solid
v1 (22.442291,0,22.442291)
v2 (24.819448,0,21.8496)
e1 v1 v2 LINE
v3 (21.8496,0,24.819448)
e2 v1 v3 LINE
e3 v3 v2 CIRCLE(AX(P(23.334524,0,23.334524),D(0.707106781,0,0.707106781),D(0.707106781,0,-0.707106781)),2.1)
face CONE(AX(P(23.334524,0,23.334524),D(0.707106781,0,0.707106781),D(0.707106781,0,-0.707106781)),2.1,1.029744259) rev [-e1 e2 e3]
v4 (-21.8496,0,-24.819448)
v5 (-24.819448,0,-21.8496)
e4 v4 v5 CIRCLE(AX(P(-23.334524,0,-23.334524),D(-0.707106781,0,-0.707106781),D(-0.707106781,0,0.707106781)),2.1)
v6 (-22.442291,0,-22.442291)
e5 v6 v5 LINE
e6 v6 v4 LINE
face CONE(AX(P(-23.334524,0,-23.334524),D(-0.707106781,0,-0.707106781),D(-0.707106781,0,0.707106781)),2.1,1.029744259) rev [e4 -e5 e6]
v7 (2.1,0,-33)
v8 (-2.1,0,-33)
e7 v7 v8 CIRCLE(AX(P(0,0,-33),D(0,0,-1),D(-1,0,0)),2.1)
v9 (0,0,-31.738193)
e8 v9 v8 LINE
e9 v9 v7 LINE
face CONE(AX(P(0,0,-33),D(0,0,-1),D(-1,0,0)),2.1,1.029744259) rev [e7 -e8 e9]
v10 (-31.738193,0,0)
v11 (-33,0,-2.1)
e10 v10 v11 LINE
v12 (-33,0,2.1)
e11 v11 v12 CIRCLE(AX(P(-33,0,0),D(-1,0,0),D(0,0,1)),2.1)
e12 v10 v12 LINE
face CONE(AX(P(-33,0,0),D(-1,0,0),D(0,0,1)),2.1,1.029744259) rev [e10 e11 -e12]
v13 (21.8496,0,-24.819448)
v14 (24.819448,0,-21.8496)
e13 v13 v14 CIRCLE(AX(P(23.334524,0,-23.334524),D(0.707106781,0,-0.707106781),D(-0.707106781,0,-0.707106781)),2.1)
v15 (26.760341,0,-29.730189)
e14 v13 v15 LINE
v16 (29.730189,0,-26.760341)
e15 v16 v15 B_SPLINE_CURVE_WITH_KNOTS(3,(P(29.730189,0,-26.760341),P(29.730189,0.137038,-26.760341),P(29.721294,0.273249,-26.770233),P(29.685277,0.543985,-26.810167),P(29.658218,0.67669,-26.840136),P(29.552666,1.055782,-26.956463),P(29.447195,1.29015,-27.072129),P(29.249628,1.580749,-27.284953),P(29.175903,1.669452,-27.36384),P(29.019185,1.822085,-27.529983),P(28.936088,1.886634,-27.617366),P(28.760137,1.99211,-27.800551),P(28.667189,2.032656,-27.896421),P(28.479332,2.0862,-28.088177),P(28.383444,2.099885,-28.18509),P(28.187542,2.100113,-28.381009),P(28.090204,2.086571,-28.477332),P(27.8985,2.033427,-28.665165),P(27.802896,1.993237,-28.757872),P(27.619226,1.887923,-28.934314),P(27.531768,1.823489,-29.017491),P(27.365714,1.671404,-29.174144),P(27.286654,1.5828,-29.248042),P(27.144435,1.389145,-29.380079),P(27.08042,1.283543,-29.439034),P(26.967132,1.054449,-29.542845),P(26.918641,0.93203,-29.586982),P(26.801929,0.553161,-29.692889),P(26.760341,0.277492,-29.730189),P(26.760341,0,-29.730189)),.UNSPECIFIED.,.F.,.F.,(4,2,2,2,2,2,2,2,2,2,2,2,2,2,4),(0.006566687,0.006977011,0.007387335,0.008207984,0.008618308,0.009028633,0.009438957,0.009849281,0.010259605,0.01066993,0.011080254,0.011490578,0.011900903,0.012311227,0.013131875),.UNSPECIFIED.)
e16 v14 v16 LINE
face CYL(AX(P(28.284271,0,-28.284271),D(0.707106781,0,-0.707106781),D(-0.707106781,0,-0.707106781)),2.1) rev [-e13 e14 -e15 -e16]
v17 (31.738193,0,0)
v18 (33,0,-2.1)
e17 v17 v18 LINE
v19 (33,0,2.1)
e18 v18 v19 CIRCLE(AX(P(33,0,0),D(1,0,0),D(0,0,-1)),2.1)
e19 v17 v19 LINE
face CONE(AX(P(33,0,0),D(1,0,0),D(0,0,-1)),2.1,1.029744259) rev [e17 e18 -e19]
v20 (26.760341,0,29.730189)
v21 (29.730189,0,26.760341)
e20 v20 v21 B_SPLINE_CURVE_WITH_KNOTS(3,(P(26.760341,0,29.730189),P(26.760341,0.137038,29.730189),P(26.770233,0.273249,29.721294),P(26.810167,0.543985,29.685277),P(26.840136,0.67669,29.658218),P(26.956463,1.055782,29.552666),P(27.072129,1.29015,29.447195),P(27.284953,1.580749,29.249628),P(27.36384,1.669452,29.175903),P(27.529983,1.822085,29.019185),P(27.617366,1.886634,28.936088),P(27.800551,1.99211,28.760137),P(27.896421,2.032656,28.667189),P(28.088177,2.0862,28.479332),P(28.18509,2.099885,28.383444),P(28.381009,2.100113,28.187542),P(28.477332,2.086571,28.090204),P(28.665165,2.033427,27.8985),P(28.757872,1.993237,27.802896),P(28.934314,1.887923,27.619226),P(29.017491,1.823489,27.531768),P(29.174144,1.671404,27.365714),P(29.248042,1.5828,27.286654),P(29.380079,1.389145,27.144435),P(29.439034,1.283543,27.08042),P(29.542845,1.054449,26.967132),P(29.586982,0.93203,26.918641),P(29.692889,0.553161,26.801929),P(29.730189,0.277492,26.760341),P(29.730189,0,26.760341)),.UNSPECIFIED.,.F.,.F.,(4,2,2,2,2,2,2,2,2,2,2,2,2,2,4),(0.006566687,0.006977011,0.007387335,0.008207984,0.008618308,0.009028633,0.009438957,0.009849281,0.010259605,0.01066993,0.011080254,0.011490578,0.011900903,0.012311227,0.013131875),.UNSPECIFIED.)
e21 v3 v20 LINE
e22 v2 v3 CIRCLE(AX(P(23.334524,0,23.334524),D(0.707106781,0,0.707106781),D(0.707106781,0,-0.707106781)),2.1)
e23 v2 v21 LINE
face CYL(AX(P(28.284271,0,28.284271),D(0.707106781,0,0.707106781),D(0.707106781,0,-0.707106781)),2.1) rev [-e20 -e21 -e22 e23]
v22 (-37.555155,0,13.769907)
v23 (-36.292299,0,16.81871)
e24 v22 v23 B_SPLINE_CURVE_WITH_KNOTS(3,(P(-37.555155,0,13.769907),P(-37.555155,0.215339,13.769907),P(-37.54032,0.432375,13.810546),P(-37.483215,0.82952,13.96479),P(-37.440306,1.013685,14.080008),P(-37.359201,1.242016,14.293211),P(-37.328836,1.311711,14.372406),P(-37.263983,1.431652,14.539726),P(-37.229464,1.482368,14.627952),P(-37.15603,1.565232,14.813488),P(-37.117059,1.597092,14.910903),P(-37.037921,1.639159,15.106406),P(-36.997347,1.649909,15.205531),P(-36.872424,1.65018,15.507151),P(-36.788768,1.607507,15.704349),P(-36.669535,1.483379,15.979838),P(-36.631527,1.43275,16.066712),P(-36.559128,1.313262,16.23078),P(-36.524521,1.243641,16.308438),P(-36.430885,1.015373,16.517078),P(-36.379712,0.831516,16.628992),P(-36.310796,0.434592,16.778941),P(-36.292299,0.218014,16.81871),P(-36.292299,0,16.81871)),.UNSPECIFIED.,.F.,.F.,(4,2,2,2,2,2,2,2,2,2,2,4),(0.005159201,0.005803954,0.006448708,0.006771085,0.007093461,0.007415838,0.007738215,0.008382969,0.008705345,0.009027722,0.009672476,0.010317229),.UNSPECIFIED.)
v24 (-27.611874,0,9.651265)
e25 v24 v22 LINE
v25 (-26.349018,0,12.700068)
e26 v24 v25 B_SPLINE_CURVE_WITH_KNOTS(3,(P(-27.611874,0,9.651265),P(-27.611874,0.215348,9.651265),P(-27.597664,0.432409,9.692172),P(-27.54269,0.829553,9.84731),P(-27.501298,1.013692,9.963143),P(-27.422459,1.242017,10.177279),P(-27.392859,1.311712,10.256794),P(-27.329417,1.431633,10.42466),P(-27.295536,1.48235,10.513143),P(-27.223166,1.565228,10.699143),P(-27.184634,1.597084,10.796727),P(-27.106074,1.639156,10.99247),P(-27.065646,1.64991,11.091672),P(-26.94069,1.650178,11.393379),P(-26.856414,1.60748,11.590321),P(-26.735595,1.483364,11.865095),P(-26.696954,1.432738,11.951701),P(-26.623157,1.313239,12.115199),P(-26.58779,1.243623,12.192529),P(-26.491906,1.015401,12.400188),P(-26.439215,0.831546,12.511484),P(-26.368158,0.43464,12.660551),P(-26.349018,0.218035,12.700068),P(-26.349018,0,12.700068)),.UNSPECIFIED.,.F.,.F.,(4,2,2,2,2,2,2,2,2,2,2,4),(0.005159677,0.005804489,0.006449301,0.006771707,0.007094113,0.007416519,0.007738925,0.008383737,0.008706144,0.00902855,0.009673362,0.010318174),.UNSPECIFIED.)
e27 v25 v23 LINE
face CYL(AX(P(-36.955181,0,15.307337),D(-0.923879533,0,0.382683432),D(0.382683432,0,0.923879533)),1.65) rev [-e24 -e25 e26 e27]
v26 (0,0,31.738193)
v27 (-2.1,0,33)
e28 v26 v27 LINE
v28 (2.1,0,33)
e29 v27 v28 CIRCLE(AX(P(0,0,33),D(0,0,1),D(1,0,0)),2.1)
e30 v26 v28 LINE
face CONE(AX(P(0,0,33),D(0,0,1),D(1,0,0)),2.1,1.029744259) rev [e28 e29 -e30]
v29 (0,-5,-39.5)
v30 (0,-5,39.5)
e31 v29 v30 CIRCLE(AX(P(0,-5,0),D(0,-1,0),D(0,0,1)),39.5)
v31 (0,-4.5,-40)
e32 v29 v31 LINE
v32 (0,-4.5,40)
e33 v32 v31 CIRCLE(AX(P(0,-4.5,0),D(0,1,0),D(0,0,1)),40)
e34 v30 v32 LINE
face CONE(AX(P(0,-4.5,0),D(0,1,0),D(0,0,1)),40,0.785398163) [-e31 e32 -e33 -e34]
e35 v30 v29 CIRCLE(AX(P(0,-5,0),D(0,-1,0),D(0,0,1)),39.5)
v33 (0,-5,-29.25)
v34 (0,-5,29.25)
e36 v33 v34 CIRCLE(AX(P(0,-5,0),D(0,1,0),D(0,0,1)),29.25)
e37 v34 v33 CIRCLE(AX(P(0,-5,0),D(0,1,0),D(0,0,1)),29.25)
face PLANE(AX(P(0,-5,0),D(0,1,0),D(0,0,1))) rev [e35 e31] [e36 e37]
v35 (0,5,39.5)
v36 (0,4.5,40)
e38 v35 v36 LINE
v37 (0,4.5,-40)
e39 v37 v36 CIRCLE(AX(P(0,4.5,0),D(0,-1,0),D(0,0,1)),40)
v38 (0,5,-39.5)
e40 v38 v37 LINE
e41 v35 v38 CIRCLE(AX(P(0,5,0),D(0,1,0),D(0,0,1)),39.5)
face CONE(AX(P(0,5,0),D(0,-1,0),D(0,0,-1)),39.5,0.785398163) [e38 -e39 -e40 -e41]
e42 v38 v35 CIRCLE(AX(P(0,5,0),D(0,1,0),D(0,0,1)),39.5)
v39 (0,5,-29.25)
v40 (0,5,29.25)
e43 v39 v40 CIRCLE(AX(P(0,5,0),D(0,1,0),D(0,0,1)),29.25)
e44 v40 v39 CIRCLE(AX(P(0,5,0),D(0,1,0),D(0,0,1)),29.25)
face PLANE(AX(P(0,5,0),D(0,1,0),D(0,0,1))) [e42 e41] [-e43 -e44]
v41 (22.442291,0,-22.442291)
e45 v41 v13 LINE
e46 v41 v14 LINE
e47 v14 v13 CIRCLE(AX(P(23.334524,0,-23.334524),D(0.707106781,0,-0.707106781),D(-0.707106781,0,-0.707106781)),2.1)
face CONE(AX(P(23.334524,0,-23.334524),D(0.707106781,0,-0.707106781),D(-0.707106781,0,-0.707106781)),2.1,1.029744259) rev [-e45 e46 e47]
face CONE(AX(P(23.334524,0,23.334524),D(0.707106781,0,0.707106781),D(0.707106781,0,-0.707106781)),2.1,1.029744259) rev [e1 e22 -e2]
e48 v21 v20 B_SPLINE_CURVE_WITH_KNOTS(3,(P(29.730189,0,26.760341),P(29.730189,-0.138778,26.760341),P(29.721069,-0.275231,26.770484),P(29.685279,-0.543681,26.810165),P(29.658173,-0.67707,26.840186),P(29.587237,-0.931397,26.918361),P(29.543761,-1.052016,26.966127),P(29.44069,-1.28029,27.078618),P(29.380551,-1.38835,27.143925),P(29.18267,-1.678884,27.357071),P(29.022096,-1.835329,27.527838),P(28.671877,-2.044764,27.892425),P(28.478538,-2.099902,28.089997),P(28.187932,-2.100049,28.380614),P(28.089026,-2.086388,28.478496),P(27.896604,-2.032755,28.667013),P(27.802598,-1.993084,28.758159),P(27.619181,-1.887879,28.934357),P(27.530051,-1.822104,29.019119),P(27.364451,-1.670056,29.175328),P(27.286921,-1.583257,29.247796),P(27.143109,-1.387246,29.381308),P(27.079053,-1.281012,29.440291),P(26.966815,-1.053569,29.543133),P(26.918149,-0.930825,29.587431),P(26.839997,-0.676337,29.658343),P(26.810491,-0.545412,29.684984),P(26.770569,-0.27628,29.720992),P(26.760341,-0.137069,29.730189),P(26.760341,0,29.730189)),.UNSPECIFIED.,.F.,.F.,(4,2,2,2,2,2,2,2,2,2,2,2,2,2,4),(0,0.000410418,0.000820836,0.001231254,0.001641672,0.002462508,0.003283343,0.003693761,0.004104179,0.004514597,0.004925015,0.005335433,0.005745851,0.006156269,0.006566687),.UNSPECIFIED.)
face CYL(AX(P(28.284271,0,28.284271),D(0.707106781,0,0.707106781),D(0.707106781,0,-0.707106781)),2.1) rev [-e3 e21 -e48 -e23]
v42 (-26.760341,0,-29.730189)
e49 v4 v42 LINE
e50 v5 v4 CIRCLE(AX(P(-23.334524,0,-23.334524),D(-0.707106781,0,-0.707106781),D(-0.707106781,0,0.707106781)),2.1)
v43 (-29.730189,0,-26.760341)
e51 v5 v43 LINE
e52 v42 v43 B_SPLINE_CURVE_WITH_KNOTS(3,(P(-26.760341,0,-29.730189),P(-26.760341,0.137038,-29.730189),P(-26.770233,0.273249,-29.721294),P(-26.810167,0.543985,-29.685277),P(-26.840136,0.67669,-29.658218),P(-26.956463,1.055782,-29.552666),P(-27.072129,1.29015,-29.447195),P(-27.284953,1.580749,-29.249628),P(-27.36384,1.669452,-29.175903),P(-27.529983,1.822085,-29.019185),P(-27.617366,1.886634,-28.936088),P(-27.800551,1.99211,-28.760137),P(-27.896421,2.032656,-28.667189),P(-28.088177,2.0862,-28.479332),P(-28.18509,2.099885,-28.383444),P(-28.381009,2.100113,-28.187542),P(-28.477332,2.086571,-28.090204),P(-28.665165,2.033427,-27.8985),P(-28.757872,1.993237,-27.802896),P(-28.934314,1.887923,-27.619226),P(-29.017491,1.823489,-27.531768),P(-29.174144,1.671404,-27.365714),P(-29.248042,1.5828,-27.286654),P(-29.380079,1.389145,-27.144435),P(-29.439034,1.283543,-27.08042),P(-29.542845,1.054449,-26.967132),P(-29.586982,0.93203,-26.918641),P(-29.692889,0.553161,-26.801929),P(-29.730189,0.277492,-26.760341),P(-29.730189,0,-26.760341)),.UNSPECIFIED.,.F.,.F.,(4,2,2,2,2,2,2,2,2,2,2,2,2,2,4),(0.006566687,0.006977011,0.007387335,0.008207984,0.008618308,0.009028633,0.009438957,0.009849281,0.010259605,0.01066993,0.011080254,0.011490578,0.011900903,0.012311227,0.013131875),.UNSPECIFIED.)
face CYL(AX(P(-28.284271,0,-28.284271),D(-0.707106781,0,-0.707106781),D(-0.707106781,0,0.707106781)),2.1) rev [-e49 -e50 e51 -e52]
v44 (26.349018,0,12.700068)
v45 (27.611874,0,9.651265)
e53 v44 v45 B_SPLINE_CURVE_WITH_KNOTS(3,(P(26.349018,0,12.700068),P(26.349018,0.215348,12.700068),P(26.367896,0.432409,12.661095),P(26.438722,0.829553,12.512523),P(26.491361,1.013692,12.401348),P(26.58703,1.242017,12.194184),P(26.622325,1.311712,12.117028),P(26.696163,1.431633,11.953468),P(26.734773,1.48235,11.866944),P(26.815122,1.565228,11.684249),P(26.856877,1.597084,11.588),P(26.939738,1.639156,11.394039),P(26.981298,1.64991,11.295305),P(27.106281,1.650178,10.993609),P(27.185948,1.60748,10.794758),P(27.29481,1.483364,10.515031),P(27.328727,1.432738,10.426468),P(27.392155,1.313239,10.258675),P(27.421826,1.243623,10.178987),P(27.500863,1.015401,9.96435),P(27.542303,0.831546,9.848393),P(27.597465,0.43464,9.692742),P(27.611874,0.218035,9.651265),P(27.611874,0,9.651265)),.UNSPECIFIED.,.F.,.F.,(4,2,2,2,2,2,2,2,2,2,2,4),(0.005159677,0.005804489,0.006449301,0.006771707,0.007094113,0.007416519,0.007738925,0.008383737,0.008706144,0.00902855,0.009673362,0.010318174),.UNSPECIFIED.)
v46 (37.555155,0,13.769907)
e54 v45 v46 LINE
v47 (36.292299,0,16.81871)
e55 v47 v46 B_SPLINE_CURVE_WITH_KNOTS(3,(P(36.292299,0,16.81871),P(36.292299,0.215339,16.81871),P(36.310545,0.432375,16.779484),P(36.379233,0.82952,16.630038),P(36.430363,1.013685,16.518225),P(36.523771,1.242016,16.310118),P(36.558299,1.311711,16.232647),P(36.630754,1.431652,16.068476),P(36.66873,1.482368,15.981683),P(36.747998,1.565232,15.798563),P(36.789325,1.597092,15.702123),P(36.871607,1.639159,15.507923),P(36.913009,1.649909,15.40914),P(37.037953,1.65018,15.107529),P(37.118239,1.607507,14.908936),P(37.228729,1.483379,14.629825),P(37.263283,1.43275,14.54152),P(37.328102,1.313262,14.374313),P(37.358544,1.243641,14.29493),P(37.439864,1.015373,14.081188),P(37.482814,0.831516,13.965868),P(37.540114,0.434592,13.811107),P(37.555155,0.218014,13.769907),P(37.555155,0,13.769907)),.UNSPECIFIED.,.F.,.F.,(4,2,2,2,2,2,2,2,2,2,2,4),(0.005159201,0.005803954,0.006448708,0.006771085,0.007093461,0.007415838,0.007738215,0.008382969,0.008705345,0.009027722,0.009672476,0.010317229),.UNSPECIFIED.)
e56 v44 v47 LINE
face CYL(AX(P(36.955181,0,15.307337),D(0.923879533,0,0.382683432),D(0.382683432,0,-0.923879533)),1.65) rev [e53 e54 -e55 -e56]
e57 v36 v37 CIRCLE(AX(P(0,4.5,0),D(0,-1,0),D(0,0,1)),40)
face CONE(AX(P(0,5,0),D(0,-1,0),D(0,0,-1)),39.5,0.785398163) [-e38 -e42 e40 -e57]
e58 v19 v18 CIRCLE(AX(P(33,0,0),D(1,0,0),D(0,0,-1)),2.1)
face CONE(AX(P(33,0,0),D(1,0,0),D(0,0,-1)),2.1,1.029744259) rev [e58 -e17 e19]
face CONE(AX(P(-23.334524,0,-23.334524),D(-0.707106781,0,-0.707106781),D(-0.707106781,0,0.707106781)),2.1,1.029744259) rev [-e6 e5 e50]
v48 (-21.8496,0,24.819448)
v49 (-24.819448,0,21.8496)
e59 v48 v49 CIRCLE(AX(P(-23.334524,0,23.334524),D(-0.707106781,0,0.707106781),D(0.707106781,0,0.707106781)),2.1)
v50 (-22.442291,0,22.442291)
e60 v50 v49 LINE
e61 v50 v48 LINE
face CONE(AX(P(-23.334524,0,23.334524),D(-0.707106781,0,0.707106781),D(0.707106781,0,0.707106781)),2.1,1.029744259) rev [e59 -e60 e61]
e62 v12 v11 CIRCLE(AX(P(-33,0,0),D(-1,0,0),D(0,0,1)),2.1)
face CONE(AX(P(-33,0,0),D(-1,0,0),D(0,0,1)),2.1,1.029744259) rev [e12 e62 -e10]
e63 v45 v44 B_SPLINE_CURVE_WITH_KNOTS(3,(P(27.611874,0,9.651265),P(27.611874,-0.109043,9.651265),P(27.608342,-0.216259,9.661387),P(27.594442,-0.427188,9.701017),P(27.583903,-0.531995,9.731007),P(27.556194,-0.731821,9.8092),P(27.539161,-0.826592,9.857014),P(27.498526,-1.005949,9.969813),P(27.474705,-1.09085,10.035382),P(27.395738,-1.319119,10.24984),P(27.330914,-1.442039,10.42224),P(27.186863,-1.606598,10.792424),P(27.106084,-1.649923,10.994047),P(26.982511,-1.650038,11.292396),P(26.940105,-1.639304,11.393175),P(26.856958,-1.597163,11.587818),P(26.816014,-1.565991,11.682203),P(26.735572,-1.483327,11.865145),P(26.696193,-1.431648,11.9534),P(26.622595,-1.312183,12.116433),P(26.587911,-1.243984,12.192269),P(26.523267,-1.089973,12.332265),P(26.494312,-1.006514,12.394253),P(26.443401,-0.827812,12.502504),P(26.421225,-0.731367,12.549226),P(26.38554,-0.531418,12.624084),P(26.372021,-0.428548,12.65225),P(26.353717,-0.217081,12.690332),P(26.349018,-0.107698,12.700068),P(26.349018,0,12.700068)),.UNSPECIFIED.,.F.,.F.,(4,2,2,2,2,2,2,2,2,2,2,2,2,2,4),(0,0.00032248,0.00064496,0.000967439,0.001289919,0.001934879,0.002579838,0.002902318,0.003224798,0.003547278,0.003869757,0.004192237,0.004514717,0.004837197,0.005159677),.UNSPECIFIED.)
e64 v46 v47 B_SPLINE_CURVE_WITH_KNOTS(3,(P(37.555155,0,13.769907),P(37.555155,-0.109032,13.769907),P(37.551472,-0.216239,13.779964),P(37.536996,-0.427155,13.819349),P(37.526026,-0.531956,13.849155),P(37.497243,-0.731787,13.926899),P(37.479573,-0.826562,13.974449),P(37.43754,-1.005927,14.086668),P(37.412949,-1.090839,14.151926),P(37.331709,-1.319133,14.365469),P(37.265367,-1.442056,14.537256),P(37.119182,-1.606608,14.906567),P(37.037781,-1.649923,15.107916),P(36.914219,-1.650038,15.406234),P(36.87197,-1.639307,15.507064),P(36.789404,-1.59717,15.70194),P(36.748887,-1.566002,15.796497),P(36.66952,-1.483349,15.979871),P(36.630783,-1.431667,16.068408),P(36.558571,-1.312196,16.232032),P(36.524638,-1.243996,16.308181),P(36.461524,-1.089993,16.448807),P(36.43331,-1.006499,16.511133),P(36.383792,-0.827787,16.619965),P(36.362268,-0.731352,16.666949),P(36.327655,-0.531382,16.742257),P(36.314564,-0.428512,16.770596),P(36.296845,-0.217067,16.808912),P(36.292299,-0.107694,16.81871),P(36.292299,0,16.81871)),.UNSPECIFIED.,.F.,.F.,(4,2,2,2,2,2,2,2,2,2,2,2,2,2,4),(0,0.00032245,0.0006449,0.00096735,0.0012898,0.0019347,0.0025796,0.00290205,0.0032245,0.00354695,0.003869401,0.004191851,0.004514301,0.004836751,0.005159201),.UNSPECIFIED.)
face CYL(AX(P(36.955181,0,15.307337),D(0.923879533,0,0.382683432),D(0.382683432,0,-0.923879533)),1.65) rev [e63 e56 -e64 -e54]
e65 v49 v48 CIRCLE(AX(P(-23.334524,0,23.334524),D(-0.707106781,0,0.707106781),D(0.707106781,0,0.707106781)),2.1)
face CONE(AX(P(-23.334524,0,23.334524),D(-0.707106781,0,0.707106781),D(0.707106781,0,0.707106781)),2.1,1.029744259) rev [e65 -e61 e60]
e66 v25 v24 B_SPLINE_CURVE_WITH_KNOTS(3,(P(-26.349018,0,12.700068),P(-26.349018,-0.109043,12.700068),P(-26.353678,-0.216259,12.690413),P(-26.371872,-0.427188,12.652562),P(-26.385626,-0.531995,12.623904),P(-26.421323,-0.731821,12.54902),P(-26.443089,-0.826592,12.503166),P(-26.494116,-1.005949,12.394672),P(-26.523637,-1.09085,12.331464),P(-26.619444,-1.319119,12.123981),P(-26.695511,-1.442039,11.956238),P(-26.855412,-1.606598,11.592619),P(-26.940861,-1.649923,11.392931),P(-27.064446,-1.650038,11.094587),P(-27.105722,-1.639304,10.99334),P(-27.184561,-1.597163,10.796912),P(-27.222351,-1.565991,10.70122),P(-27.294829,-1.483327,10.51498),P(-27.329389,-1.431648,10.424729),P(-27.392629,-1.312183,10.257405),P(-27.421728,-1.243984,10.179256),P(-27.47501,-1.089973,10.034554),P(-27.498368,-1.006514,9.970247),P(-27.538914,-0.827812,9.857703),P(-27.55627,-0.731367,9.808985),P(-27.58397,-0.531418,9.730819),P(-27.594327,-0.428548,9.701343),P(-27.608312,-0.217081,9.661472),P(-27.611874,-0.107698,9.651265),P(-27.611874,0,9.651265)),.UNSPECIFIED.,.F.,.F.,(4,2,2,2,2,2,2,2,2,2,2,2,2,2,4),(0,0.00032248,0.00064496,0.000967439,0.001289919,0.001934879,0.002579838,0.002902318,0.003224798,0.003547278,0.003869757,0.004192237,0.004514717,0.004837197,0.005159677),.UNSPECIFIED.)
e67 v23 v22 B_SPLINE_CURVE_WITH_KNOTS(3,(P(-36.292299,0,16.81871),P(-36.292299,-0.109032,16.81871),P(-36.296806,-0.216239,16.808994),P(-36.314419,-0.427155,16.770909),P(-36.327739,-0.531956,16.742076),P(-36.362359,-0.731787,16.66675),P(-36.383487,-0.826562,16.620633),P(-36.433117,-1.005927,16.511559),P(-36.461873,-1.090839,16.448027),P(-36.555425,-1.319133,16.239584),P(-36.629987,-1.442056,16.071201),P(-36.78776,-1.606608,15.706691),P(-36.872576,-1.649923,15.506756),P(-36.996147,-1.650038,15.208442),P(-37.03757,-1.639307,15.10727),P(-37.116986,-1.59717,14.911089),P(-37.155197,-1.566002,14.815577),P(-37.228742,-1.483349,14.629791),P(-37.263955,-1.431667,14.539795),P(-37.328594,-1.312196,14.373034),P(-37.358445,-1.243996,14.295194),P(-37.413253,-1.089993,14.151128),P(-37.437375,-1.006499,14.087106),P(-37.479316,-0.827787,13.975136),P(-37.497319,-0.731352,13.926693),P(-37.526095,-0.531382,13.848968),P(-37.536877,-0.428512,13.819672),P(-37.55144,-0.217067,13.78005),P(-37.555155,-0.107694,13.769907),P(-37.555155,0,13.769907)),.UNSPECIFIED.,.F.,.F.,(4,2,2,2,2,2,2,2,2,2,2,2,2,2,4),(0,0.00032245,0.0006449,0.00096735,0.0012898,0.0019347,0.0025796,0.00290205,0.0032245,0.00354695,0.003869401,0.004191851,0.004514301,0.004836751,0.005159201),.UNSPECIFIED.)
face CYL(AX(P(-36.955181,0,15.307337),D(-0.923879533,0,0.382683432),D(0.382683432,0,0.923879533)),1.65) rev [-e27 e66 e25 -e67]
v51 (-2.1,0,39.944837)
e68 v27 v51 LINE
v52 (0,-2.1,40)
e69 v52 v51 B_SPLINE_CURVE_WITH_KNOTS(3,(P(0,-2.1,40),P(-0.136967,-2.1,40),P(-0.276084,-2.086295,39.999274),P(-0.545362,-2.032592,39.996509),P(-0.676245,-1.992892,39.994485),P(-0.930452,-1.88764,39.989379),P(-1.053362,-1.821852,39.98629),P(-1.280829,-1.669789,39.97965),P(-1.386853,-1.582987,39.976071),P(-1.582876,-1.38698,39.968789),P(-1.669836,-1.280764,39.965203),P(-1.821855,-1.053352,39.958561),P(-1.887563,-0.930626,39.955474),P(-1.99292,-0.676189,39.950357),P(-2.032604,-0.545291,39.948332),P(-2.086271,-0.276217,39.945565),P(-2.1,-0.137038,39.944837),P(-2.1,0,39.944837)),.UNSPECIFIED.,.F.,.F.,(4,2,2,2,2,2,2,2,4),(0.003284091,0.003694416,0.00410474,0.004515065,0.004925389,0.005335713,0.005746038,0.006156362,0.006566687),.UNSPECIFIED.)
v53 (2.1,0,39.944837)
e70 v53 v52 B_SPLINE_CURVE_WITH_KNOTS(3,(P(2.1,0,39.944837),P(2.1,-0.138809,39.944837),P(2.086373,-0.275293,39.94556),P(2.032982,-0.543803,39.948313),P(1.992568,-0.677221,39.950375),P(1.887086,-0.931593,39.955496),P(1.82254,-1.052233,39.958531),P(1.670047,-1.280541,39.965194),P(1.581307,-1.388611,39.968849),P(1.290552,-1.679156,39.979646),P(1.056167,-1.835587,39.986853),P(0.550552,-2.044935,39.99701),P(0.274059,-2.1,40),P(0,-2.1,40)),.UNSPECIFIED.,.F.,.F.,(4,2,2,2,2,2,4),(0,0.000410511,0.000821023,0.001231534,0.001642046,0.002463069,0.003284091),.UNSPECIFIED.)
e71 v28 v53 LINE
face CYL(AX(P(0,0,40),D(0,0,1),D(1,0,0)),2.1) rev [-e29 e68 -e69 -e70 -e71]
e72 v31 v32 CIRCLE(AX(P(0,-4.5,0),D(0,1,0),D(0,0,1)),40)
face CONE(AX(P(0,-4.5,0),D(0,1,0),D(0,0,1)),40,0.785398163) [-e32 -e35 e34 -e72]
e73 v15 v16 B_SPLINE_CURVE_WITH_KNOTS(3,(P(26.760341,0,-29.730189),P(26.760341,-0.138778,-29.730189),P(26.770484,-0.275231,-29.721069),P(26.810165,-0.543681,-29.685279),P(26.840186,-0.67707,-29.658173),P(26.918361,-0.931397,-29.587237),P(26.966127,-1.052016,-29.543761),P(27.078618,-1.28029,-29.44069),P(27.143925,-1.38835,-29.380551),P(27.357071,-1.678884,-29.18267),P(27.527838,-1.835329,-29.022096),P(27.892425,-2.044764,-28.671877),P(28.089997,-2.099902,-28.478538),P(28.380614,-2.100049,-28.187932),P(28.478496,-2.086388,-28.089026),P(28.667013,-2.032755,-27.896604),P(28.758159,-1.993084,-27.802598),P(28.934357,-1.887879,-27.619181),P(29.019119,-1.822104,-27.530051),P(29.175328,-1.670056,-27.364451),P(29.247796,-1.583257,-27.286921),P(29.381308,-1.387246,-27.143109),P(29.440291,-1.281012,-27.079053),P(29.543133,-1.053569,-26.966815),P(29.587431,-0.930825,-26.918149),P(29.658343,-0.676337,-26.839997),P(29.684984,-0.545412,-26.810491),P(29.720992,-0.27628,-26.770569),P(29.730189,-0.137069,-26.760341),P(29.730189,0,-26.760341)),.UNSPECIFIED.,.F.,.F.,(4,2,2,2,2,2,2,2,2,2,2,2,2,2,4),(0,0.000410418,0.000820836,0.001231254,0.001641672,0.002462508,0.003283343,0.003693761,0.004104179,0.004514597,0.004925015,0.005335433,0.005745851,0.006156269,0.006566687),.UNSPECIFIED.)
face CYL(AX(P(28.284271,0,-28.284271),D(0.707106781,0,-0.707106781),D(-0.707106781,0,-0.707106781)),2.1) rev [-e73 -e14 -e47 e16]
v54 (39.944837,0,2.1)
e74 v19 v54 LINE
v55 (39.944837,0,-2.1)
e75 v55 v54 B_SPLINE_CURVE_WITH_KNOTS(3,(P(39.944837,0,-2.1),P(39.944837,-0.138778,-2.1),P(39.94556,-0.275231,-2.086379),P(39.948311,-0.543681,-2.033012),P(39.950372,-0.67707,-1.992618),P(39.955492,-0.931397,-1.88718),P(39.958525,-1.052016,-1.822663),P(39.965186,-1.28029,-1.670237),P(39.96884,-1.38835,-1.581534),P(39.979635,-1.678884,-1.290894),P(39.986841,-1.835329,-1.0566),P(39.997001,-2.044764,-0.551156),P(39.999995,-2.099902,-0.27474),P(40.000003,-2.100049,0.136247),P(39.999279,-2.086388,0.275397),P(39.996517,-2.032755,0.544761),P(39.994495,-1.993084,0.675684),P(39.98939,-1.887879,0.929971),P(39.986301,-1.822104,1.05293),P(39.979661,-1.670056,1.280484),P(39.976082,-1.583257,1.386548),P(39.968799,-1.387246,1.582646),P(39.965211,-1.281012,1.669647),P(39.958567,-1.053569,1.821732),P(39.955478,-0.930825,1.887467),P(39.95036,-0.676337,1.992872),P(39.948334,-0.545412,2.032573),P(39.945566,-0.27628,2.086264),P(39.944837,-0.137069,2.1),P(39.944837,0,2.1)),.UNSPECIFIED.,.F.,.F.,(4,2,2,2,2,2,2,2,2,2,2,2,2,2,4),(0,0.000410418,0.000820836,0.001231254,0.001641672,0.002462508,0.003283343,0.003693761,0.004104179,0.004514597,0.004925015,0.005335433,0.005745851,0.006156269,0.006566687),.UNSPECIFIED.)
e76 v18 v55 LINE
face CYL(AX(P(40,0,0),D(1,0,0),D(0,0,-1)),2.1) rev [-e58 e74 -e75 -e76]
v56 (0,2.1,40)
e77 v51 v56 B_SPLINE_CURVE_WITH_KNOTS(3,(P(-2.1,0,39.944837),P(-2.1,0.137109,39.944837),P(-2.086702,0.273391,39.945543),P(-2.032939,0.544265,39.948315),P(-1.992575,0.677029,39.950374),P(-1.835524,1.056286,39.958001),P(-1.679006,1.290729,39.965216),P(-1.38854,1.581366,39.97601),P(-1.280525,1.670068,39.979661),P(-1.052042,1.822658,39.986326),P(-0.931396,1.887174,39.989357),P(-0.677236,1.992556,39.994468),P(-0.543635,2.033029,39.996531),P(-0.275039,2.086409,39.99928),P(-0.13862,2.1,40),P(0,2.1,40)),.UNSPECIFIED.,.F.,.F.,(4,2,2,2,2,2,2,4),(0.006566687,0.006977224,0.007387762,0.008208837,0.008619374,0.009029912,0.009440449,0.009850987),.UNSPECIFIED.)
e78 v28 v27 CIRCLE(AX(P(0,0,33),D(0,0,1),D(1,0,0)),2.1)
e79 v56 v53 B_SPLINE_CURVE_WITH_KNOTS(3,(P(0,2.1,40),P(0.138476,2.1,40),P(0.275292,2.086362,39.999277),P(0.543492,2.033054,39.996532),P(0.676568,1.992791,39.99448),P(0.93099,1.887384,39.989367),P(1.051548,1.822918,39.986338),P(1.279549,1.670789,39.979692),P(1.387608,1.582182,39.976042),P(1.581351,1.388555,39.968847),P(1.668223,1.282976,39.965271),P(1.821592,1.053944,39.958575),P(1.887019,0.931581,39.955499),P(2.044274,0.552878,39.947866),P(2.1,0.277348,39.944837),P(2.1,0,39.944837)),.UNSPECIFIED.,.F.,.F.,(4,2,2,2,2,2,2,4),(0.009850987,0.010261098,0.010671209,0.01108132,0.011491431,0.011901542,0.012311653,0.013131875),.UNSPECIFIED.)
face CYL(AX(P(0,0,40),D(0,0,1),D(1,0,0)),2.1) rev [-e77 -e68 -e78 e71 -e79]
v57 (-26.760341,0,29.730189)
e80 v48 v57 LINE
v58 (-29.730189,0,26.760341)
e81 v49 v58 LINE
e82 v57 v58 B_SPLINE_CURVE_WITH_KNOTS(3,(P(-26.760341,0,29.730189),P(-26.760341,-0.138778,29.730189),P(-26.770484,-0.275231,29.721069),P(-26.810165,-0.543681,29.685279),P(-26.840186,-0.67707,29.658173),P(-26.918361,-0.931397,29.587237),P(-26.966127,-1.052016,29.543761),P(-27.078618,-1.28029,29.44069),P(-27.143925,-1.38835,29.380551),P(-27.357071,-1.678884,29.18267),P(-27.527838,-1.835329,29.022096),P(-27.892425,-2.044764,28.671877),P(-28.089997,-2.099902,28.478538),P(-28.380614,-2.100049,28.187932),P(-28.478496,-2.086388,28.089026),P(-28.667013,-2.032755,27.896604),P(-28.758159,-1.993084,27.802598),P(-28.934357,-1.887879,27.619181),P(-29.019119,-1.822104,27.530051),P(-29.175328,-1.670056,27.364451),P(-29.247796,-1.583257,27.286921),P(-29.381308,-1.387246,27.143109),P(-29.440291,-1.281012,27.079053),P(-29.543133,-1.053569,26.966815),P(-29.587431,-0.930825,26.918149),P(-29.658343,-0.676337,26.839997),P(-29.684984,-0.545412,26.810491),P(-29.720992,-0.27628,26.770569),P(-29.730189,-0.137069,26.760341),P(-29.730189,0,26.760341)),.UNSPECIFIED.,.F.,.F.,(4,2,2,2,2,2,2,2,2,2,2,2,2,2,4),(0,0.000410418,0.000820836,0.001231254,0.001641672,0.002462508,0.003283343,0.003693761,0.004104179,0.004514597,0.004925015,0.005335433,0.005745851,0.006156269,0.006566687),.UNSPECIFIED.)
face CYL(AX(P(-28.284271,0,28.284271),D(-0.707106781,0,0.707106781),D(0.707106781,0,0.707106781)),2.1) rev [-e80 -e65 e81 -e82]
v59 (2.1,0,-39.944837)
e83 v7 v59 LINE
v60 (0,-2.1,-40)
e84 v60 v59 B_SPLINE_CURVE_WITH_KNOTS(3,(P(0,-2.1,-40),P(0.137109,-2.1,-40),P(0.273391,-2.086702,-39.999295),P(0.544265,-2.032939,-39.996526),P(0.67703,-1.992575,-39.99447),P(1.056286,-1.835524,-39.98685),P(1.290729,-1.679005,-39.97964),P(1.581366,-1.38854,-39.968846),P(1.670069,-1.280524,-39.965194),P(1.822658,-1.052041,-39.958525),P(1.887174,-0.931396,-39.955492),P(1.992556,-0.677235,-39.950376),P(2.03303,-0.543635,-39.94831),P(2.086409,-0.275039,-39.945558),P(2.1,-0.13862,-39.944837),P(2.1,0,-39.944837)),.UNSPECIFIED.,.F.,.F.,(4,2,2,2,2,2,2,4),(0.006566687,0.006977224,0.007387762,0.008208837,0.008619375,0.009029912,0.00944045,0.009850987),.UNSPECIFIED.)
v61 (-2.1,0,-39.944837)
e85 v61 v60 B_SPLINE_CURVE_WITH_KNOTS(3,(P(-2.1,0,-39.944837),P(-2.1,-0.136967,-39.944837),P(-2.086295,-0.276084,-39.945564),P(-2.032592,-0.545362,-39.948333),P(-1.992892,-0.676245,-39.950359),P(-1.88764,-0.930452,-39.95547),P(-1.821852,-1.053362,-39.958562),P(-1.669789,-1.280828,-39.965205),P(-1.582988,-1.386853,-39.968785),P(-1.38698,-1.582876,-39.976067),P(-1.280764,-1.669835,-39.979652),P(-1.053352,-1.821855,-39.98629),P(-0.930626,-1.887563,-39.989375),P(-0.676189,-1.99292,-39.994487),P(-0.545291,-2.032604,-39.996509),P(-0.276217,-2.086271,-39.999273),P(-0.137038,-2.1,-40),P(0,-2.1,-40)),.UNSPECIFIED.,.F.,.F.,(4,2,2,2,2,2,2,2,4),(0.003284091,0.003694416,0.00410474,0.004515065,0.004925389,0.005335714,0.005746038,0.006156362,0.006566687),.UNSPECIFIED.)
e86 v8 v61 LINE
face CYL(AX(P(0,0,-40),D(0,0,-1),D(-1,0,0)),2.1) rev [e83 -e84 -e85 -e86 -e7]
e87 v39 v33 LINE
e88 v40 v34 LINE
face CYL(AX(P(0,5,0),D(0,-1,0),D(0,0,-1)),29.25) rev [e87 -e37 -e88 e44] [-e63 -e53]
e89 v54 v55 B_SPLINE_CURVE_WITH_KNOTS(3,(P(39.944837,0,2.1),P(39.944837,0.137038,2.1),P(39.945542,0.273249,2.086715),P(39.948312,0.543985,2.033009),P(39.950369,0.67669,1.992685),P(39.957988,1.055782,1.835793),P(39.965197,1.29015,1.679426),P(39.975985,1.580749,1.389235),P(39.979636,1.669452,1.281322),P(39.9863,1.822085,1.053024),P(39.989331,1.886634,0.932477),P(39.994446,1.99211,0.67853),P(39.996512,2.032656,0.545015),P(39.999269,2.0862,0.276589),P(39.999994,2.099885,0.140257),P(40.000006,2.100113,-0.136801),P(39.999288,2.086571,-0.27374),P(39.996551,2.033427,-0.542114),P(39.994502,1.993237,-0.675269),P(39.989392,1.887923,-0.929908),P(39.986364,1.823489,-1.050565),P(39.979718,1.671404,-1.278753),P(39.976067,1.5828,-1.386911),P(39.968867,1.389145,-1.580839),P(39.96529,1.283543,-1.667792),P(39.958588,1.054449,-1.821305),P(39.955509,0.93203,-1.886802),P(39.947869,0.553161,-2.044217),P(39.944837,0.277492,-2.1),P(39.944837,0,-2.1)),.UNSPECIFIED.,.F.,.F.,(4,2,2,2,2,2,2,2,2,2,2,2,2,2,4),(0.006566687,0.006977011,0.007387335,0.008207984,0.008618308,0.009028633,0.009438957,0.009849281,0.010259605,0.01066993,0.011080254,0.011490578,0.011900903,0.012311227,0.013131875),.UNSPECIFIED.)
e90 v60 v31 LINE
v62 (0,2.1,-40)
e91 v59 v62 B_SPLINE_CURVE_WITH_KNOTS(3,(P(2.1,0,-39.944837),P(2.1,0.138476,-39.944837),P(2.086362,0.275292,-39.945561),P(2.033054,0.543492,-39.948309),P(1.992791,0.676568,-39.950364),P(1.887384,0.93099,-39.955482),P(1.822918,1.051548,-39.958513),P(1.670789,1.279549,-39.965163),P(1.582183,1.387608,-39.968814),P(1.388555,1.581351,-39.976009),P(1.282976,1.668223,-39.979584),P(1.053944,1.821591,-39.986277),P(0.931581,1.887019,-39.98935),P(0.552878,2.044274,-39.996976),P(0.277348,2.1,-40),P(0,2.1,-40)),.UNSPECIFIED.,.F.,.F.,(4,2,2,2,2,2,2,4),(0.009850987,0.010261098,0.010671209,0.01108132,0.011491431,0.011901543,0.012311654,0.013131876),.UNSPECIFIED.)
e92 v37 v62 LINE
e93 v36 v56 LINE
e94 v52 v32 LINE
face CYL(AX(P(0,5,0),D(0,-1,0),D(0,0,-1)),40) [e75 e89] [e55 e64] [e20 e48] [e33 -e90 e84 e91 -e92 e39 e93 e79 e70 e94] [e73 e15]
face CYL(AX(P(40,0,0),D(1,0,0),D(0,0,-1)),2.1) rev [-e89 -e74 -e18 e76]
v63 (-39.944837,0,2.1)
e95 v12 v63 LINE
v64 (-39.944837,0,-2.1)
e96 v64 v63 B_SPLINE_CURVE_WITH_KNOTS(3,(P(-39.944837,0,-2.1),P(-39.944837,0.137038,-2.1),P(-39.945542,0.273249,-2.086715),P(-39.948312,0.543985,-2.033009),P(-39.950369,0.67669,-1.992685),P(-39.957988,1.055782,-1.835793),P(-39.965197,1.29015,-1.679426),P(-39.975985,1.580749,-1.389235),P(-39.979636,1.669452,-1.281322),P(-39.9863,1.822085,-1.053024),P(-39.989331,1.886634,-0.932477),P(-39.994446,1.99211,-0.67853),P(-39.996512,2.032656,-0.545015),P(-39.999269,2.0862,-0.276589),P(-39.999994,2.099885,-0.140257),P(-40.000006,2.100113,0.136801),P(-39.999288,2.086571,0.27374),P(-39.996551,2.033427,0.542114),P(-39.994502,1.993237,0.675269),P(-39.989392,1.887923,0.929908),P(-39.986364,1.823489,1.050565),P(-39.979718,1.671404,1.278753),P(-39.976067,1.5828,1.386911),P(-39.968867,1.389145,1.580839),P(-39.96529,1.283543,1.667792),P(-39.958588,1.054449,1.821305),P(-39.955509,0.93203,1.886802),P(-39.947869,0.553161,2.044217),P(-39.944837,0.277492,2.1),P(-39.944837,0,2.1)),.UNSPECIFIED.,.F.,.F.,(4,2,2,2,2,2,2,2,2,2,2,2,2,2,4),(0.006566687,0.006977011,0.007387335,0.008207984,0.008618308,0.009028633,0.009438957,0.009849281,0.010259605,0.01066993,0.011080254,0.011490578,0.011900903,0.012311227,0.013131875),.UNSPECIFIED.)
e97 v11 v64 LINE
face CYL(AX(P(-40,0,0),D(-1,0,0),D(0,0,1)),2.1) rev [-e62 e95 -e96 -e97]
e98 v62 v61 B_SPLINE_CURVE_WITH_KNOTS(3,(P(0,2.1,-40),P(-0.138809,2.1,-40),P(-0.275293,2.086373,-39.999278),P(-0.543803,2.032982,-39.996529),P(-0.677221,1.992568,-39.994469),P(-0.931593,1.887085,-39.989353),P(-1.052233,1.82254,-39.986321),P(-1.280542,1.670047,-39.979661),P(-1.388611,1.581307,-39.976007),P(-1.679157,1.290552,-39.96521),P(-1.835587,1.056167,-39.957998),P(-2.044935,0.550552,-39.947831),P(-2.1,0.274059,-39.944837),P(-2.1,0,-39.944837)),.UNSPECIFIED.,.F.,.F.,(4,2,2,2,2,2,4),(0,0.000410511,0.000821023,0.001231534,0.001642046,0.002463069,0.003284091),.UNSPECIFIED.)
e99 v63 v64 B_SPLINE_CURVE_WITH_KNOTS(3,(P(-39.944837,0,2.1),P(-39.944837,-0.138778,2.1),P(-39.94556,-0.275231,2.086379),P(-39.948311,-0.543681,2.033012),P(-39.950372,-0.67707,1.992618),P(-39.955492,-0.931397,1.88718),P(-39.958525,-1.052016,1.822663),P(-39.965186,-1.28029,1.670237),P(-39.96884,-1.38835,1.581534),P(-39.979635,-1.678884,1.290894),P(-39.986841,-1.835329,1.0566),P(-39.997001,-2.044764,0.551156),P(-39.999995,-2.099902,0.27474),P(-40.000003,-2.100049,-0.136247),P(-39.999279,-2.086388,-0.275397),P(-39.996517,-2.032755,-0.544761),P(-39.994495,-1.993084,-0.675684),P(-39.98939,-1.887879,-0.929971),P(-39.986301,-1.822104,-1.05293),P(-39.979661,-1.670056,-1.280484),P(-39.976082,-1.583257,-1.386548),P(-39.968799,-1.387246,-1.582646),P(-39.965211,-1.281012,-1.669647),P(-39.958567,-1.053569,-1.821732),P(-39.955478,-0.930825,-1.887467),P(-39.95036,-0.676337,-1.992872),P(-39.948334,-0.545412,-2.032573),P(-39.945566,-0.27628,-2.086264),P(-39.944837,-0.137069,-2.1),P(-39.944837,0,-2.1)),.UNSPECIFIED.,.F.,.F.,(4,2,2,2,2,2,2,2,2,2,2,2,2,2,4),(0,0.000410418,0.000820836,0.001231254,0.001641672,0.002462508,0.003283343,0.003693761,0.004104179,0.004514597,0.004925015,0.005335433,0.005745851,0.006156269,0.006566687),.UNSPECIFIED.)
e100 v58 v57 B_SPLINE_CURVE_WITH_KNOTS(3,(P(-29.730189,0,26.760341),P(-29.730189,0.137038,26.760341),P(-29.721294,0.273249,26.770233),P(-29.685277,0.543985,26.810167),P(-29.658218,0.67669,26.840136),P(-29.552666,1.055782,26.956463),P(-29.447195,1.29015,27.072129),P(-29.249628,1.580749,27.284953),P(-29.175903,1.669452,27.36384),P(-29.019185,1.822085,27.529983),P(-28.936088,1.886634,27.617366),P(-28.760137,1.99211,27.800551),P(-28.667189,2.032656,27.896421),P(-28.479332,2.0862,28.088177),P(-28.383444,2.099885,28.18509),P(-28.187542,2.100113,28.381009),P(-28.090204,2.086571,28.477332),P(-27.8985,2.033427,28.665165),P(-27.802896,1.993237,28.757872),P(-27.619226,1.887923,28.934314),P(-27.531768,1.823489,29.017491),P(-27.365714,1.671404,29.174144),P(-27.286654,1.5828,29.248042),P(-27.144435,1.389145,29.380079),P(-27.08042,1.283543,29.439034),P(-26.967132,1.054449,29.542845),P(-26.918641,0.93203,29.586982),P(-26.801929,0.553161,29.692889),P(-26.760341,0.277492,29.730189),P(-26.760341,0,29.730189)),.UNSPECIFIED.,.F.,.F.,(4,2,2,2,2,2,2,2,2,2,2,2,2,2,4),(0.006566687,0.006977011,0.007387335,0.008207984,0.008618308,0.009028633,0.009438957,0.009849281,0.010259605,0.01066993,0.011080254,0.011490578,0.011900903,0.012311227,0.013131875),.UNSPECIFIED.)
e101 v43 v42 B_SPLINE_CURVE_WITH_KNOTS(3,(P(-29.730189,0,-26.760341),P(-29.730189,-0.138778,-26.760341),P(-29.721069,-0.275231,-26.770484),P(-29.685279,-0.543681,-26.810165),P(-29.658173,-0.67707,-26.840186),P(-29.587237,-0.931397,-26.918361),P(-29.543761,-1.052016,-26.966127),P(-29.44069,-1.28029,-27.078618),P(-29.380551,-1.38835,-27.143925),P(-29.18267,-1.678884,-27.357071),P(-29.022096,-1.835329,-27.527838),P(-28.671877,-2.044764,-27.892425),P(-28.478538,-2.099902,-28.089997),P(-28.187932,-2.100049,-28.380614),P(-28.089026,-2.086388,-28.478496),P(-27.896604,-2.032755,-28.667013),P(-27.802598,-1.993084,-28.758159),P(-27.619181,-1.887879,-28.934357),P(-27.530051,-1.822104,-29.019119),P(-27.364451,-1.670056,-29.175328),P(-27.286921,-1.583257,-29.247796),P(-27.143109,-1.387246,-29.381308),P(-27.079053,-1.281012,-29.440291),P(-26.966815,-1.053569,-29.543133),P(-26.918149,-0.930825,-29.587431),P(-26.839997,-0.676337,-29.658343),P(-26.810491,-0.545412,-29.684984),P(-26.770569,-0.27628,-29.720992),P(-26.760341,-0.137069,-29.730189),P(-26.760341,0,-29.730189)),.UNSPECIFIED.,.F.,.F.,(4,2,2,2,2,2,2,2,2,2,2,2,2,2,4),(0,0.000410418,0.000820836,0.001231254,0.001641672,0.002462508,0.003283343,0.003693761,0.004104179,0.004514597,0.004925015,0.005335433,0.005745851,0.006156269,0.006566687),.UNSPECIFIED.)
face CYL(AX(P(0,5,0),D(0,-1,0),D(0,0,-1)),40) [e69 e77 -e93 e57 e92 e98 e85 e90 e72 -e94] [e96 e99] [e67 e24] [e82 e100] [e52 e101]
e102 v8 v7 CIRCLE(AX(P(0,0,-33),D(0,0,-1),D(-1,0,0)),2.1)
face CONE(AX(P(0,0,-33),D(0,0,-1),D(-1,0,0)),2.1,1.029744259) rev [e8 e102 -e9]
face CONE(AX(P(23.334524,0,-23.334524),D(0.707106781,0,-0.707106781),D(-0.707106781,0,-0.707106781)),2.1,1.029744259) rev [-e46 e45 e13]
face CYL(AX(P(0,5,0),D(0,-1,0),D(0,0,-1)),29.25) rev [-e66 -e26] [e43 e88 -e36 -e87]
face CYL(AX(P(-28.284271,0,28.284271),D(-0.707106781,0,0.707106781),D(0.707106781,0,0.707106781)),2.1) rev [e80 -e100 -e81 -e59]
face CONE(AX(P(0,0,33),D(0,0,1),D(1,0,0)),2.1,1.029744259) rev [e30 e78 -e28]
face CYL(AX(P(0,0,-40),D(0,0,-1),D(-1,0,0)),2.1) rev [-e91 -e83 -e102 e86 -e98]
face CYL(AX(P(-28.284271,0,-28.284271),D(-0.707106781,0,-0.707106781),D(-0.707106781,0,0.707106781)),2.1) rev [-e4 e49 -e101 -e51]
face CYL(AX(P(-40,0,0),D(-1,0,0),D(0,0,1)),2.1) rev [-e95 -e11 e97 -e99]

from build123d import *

# Parameters (mm, degrees)
SKETCH1_R              = 40
SKETCH1_R_2            = 29.25
BOSS_EXTRUDE1_DEPTH    = 5
CIRPATTERN1_COUNT      = 8
M4_TAPPED_HOLE1_REACH  = 96.9
M4_TAPPED_HOLE1_BORE_R = 1.65
CIRPATTERN2_COUNT      = 2
CIRPATTERN2_ANGLE      = 135
CHAMFER1_SIZE          = 0.5


with BuildPart() as part:
    # Sketch1 → Boss-Extrude1 (new, symmetric)
    with BuildSketch(Plane(origin=(0, 0, 0), x_dir=(1, 0, 0), z_dir=(0, 1, 0))):
        with Locations(Location((0, 0, 0), (0, 0, 270))):
            Circle(SKETCH1_R)
        with Locations(Location((0, 0, 0), (0, 0, 270))):
            Circle(SKETCH1_R_2, mode=Mode.SUBTRACT)
    extrude(amount=BOSS_EXTRUDE1_DEPTH, both=True)

    # Sketch2 → Ø4.2 (4.2) Diameter Hole1 (revolve, cut)
    with BuildSketch(Plane(origin=(0, 0, 40), x_dir=(0, -1, 0), z_dir=(1, 0, 0))):
        Polygon((0, 0), (0, 8.2618073), (2.1, 7), (2.1, 0), align=None)
    f_4_2_4_2_diameter_hole1 = revolve(axis=Axis((0, 0, 46.35), (0, 0, -1)), mode=Mode.SUBTRACT)

    # CirPattern1: Ø4.2 (4.2) Diameter Hole1 ×8 about axis
    cirpattern1_axis = Axis((0, 5, 0), (0, -1, 0))
    for i in range(1, CIRPATTERN1_COUNT):
        add(f_4_2_4_2_diameter_hole1.rotate(cirpattern1_axis, i * 360 / CIRPATTERN1_COUNT), mode=Mode.SUBTRACT)

    # M4 Tapped Hole1 bore → M4 Tapped Hole1 (cut, up to next)
    with BuildSketch(Plane(origin=(36.9551813, 0, 15.307337295), x_dir=(0.3826834323650906, 0, -0.9238795325112865), z_dir=(0.9238795325112864, 0, 0.38268343236509056)), mode=Mode.PRIVATE) as m4_tapped_hole1_sk1:
        Circle(M4_TAPPED_HOLE1_BORE_R)
    m4_tapped_hole1_tool1 = extrude(m4_tapped_hole1_sk1.sketch, amount=-M4_TAPPED_HOLE1_REACH, mode=Mode.PRIVATE) & part.part
    m4_tapped_hole1 = m4_tapped_hole1_tool1.solids().sort_by_distance((36.955181, 0, 15.307337))[0]
    add(m4_tapped_hole1, mode=Mode.SUBTRACT)

    # CirPattern2: M4 Tapped Hole1 ×2 about axis
    cirpattern2_axis = Axis((0, 5, 0), (0, -1, 0))
    for i in range(1, CIRPATTERN2_COUNT):
        add(m4_tapped_hole1.rotate(cirpattern2_axis, i * CIRPATTERN2_ANGLE / (CIRPATTERN2_COUNT - 1)), mode=Mode.SUBTRACT)

    # Chamfer1
    chamfer1_edges = [part.edges().sort_by_distance(p)[0] for p in [
        (0, -5, -40),
        (0, 5, -40),
    ]]
    chamfer(chamfer1_edges, length=CHAMFER1_SIZE)


solid = part.part
